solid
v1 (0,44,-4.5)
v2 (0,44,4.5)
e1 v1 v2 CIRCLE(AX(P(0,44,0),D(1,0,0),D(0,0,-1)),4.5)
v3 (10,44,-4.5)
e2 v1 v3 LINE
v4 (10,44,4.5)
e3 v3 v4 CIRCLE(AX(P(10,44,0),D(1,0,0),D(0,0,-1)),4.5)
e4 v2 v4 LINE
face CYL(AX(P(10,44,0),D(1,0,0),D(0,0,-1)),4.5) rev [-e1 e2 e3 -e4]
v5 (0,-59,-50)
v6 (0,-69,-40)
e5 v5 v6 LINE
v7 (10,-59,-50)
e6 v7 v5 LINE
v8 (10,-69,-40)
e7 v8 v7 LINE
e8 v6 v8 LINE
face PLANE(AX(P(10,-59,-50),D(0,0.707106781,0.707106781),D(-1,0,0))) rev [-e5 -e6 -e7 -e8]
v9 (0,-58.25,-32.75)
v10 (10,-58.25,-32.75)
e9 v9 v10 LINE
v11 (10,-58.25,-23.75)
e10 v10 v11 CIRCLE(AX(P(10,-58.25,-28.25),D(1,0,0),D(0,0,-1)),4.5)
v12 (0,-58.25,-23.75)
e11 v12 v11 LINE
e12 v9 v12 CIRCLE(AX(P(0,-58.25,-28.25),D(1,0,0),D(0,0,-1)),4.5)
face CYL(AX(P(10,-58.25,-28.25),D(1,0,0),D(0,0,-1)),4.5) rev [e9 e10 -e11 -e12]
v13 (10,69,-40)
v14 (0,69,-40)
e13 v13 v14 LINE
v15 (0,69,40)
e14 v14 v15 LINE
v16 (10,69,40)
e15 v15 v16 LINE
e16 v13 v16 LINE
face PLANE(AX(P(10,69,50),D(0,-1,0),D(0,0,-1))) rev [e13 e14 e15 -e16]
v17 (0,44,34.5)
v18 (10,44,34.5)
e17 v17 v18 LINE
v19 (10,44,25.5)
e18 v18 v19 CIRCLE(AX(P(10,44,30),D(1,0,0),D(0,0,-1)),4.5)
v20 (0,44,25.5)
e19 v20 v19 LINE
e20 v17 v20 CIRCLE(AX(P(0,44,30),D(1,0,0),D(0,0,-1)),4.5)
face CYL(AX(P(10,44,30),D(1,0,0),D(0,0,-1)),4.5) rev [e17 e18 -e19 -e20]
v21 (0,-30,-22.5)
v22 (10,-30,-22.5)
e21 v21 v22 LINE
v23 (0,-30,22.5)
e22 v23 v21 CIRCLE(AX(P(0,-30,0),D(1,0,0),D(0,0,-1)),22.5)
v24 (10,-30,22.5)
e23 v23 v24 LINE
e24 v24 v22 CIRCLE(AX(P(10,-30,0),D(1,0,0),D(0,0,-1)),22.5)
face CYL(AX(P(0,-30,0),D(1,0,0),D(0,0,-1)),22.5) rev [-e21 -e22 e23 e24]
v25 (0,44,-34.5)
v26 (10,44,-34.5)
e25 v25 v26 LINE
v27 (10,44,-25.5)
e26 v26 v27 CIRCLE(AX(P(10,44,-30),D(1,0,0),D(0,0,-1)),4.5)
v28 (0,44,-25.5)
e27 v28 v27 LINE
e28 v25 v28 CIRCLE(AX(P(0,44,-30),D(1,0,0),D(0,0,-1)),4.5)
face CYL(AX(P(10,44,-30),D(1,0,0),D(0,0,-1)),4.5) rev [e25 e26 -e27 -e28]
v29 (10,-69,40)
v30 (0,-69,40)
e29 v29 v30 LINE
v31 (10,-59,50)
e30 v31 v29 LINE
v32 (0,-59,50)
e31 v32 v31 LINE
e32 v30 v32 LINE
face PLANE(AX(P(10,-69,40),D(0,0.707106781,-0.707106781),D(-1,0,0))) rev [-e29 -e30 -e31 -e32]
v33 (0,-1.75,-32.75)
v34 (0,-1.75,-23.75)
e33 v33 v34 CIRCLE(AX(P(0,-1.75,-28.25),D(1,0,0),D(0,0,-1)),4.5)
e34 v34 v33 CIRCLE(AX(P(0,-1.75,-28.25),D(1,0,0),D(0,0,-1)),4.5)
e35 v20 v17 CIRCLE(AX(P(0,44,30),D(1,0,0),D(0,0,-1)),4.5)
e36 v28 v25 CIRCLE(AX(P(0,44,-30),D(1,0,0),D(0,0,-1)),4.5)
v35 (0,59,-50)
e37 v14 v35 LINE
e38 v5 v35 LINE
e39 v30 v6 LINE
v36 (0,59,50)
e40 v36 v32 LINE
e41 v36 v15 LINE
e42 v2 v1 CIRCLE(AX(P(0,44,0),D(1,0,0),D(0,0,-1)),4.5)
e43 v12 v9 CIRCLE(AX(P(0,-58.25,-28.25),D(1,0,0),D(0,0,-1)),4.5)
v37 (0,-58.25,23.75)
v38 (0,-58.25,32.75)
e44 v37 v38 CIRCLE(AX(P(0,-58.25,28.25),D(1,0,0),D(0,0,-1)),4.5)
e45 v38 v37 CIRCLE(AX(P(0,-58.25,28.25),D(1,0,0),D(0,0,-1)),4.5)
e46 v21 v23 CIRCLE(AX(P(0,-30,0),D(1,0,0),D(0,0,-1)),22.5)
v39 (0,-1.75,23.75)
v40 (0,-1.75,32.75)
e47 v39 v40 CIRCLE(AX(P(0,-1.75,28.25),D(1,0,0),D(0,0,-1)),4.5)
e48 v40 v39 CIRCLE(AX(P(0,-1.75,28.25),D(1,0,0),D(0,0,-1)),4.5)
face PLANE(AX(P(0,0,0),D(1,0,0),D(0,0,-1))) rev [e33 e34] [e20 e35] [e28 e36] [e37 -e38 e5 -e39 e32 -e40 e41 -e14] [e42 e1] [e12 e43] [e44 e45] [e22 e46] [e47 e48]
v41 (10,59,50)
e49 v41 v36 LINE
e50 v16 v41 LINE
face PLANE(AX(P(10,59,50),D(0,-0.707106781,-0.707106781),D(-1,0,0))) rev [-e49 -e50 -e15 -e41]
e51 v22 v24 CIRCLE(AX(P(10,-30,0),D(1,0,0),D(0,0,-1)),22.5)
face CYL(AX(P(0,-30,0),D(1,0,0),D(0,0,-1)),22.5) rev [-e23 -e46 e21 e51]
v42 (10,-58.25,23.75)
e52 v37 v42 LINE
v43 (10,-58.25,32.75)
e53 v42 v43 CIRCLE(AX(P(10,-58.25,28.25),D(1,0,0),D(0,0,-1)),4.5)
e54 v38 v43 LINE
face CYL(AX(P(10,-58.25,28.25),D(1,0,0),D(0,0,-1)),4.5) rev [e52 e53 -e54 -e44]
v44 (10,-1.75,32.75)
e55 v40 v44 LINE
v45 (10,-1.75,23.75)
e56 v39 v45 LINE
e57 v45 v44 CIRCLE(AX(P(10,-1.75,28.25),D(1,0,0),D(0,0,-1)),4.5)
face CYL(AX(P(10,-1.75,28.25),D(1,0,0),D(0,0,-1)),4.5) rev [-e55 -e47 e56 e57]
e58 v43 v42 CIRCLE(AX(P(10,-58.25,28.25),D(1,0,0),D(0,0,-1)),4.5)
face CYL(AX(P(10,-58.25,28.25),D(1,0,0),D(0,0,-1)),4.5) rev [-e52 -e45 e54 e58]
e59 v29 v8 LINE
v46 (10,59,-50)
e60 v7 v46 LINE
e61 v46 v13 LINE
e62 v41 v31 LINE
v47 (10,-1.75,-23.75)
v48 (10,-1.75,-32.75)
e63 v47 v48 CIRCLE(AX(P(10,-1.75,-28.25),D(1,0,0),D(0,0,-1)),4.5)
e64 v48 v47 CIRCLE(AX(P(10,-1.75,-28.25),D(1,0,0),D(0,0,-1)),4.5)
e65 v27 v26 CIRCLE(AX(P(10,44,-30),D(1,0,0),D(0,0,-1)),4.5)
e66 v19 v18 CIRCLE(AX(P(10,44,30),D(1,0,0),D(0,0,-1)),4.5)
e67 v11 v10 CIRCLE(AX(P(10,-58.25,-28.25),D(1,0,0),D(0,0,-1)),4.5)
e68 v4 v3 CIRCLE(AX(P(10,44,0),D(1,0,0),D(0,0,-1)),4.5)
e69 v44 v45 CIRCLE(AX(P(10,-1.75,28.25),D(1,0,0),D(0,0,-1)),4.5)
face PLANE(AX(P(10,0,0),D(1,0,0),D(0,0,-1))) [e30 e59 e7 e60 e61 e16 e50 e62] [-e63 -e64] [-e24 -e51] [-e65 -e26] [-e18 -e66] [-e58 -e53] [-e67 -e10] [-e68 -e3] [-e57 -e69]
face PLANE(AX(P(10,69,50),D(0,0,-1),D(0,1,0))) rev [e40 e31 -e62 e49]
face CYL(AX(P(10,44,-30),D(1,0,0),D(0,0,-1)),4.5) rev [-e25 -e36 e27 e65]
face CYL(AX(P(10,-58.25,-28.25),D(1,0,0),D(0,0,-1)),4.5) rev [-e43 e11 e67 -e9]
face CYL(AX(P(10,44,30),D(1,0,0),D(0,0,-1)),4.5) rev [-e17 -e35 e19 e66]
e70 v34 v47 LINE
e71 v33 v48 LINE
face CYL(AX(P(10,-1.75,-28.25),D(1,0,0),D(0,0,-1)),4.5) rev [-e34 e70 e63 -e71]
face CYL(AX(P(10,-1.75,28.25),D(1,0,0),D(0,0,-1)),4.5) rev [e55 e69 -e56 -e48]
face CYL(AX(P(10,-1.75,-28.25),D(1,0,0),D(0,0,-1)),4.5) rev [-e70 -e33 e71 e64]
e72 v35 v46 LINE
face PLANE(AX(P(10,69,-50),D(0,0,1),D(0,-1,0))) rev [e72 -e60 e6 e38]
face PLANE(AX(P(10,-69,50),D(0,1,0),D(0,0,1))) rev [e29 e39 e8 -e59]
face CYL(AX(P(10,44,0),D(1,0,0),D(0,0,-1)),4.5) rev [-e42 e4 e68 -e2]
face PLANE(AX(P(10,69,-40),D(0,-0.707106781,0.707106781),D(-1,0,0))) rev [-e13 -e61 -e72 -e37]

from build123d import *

# Parameters (mm, degrees)
SKETCH_1_W               = 100
SKETCH_1_H               = 138
EXTRUDE_1_DEPTH          = 10
HOLE_WIZARD_9_0_9_1_D    = 9
SKETCH_4_R               = 22.5
CUT_EXTRUDE_1_DEPTH      = 10
HOLE_WIZARD_9_0_9_2_D    = 9
PATTERN_CIRCULAR_1_COUNT = 4
CHAMFER_1_SIZE           = 10


with BuildPart() as part:
    # 草图1 → 凸台-拉伸1 (new body)
    with BuildSketch(Plane(origin=(0, 0, 0), x_dir=(0, 0, -1), z_dir=(1, 0, 0))):
        Rectangle(SKETCH_1_W, SKETCH_1_H)
    extrude(amount=EXTRUDE_1_DEPTH)

    # Ø9.0 (9) 直径孔1 (through all)
    with Locations(Plane(origin=(10, 0, 0), x_dir=(0, 0, -1), z_dir=(1, 0, 0))):
        with Locations((-30, 44), (0, 44), (30, 44)):
            Hole(HOLE_WIZARD_9_0_9_1_D / 2)

    # 草图4 → 切除-拉伸1 (cut)
    with BuildSketch(Plane(origin=(10, 0, 0), x_dir=(0, 0, -1), z_dir=(1, 0, 0))):
        with Locations((0, -30)):
            Circle(SKETCH_4_R)
    extrude(amount=-CUT_EXTRUDE_1_DEPTH, mode=Mode.SUBTRACT)

    # Ø9.0 (9) 直径孔2 (through all)
    with Locations(Plane(origin=(10, 0, 0), x_dir=(0, 0, -1), z_dir=(1, 0, 0))):
        with Locations((-28.25, -1.75)):
            hole_wizard_9_0_9_2 = Hole(HOLE_WIZARD_9_0_9_2_D / 2)

    # 阵列(圆周)1: Ø9.0 (9) 直径孔2 ×4 about axis
    pattern_circular_1_axis = Axis((0, -30, 0), (1, 0, 0))
    for i in range(1, PATTERN_CIRCULAR_1_COUNT):
        add(hole_wizard_9_0_9_2.rotate(pattern_circular_1_axis, i * 360 / PATTERN_CIRCULAR_1_COUNT), mode=Mode.SUBTRACT)

    # 倒角1
    chamfer_1_edges = [part.edges().sort_by_distance(p)[0] for p in [
        (5, -69, -50),
        (5, -69, 50),
        (5, 69, 50),
        (5, 69, -50),
    ]]
    chamfer(chamfer_1_edges, length=CHAMFER_1_SIZE)


solid = part.part
